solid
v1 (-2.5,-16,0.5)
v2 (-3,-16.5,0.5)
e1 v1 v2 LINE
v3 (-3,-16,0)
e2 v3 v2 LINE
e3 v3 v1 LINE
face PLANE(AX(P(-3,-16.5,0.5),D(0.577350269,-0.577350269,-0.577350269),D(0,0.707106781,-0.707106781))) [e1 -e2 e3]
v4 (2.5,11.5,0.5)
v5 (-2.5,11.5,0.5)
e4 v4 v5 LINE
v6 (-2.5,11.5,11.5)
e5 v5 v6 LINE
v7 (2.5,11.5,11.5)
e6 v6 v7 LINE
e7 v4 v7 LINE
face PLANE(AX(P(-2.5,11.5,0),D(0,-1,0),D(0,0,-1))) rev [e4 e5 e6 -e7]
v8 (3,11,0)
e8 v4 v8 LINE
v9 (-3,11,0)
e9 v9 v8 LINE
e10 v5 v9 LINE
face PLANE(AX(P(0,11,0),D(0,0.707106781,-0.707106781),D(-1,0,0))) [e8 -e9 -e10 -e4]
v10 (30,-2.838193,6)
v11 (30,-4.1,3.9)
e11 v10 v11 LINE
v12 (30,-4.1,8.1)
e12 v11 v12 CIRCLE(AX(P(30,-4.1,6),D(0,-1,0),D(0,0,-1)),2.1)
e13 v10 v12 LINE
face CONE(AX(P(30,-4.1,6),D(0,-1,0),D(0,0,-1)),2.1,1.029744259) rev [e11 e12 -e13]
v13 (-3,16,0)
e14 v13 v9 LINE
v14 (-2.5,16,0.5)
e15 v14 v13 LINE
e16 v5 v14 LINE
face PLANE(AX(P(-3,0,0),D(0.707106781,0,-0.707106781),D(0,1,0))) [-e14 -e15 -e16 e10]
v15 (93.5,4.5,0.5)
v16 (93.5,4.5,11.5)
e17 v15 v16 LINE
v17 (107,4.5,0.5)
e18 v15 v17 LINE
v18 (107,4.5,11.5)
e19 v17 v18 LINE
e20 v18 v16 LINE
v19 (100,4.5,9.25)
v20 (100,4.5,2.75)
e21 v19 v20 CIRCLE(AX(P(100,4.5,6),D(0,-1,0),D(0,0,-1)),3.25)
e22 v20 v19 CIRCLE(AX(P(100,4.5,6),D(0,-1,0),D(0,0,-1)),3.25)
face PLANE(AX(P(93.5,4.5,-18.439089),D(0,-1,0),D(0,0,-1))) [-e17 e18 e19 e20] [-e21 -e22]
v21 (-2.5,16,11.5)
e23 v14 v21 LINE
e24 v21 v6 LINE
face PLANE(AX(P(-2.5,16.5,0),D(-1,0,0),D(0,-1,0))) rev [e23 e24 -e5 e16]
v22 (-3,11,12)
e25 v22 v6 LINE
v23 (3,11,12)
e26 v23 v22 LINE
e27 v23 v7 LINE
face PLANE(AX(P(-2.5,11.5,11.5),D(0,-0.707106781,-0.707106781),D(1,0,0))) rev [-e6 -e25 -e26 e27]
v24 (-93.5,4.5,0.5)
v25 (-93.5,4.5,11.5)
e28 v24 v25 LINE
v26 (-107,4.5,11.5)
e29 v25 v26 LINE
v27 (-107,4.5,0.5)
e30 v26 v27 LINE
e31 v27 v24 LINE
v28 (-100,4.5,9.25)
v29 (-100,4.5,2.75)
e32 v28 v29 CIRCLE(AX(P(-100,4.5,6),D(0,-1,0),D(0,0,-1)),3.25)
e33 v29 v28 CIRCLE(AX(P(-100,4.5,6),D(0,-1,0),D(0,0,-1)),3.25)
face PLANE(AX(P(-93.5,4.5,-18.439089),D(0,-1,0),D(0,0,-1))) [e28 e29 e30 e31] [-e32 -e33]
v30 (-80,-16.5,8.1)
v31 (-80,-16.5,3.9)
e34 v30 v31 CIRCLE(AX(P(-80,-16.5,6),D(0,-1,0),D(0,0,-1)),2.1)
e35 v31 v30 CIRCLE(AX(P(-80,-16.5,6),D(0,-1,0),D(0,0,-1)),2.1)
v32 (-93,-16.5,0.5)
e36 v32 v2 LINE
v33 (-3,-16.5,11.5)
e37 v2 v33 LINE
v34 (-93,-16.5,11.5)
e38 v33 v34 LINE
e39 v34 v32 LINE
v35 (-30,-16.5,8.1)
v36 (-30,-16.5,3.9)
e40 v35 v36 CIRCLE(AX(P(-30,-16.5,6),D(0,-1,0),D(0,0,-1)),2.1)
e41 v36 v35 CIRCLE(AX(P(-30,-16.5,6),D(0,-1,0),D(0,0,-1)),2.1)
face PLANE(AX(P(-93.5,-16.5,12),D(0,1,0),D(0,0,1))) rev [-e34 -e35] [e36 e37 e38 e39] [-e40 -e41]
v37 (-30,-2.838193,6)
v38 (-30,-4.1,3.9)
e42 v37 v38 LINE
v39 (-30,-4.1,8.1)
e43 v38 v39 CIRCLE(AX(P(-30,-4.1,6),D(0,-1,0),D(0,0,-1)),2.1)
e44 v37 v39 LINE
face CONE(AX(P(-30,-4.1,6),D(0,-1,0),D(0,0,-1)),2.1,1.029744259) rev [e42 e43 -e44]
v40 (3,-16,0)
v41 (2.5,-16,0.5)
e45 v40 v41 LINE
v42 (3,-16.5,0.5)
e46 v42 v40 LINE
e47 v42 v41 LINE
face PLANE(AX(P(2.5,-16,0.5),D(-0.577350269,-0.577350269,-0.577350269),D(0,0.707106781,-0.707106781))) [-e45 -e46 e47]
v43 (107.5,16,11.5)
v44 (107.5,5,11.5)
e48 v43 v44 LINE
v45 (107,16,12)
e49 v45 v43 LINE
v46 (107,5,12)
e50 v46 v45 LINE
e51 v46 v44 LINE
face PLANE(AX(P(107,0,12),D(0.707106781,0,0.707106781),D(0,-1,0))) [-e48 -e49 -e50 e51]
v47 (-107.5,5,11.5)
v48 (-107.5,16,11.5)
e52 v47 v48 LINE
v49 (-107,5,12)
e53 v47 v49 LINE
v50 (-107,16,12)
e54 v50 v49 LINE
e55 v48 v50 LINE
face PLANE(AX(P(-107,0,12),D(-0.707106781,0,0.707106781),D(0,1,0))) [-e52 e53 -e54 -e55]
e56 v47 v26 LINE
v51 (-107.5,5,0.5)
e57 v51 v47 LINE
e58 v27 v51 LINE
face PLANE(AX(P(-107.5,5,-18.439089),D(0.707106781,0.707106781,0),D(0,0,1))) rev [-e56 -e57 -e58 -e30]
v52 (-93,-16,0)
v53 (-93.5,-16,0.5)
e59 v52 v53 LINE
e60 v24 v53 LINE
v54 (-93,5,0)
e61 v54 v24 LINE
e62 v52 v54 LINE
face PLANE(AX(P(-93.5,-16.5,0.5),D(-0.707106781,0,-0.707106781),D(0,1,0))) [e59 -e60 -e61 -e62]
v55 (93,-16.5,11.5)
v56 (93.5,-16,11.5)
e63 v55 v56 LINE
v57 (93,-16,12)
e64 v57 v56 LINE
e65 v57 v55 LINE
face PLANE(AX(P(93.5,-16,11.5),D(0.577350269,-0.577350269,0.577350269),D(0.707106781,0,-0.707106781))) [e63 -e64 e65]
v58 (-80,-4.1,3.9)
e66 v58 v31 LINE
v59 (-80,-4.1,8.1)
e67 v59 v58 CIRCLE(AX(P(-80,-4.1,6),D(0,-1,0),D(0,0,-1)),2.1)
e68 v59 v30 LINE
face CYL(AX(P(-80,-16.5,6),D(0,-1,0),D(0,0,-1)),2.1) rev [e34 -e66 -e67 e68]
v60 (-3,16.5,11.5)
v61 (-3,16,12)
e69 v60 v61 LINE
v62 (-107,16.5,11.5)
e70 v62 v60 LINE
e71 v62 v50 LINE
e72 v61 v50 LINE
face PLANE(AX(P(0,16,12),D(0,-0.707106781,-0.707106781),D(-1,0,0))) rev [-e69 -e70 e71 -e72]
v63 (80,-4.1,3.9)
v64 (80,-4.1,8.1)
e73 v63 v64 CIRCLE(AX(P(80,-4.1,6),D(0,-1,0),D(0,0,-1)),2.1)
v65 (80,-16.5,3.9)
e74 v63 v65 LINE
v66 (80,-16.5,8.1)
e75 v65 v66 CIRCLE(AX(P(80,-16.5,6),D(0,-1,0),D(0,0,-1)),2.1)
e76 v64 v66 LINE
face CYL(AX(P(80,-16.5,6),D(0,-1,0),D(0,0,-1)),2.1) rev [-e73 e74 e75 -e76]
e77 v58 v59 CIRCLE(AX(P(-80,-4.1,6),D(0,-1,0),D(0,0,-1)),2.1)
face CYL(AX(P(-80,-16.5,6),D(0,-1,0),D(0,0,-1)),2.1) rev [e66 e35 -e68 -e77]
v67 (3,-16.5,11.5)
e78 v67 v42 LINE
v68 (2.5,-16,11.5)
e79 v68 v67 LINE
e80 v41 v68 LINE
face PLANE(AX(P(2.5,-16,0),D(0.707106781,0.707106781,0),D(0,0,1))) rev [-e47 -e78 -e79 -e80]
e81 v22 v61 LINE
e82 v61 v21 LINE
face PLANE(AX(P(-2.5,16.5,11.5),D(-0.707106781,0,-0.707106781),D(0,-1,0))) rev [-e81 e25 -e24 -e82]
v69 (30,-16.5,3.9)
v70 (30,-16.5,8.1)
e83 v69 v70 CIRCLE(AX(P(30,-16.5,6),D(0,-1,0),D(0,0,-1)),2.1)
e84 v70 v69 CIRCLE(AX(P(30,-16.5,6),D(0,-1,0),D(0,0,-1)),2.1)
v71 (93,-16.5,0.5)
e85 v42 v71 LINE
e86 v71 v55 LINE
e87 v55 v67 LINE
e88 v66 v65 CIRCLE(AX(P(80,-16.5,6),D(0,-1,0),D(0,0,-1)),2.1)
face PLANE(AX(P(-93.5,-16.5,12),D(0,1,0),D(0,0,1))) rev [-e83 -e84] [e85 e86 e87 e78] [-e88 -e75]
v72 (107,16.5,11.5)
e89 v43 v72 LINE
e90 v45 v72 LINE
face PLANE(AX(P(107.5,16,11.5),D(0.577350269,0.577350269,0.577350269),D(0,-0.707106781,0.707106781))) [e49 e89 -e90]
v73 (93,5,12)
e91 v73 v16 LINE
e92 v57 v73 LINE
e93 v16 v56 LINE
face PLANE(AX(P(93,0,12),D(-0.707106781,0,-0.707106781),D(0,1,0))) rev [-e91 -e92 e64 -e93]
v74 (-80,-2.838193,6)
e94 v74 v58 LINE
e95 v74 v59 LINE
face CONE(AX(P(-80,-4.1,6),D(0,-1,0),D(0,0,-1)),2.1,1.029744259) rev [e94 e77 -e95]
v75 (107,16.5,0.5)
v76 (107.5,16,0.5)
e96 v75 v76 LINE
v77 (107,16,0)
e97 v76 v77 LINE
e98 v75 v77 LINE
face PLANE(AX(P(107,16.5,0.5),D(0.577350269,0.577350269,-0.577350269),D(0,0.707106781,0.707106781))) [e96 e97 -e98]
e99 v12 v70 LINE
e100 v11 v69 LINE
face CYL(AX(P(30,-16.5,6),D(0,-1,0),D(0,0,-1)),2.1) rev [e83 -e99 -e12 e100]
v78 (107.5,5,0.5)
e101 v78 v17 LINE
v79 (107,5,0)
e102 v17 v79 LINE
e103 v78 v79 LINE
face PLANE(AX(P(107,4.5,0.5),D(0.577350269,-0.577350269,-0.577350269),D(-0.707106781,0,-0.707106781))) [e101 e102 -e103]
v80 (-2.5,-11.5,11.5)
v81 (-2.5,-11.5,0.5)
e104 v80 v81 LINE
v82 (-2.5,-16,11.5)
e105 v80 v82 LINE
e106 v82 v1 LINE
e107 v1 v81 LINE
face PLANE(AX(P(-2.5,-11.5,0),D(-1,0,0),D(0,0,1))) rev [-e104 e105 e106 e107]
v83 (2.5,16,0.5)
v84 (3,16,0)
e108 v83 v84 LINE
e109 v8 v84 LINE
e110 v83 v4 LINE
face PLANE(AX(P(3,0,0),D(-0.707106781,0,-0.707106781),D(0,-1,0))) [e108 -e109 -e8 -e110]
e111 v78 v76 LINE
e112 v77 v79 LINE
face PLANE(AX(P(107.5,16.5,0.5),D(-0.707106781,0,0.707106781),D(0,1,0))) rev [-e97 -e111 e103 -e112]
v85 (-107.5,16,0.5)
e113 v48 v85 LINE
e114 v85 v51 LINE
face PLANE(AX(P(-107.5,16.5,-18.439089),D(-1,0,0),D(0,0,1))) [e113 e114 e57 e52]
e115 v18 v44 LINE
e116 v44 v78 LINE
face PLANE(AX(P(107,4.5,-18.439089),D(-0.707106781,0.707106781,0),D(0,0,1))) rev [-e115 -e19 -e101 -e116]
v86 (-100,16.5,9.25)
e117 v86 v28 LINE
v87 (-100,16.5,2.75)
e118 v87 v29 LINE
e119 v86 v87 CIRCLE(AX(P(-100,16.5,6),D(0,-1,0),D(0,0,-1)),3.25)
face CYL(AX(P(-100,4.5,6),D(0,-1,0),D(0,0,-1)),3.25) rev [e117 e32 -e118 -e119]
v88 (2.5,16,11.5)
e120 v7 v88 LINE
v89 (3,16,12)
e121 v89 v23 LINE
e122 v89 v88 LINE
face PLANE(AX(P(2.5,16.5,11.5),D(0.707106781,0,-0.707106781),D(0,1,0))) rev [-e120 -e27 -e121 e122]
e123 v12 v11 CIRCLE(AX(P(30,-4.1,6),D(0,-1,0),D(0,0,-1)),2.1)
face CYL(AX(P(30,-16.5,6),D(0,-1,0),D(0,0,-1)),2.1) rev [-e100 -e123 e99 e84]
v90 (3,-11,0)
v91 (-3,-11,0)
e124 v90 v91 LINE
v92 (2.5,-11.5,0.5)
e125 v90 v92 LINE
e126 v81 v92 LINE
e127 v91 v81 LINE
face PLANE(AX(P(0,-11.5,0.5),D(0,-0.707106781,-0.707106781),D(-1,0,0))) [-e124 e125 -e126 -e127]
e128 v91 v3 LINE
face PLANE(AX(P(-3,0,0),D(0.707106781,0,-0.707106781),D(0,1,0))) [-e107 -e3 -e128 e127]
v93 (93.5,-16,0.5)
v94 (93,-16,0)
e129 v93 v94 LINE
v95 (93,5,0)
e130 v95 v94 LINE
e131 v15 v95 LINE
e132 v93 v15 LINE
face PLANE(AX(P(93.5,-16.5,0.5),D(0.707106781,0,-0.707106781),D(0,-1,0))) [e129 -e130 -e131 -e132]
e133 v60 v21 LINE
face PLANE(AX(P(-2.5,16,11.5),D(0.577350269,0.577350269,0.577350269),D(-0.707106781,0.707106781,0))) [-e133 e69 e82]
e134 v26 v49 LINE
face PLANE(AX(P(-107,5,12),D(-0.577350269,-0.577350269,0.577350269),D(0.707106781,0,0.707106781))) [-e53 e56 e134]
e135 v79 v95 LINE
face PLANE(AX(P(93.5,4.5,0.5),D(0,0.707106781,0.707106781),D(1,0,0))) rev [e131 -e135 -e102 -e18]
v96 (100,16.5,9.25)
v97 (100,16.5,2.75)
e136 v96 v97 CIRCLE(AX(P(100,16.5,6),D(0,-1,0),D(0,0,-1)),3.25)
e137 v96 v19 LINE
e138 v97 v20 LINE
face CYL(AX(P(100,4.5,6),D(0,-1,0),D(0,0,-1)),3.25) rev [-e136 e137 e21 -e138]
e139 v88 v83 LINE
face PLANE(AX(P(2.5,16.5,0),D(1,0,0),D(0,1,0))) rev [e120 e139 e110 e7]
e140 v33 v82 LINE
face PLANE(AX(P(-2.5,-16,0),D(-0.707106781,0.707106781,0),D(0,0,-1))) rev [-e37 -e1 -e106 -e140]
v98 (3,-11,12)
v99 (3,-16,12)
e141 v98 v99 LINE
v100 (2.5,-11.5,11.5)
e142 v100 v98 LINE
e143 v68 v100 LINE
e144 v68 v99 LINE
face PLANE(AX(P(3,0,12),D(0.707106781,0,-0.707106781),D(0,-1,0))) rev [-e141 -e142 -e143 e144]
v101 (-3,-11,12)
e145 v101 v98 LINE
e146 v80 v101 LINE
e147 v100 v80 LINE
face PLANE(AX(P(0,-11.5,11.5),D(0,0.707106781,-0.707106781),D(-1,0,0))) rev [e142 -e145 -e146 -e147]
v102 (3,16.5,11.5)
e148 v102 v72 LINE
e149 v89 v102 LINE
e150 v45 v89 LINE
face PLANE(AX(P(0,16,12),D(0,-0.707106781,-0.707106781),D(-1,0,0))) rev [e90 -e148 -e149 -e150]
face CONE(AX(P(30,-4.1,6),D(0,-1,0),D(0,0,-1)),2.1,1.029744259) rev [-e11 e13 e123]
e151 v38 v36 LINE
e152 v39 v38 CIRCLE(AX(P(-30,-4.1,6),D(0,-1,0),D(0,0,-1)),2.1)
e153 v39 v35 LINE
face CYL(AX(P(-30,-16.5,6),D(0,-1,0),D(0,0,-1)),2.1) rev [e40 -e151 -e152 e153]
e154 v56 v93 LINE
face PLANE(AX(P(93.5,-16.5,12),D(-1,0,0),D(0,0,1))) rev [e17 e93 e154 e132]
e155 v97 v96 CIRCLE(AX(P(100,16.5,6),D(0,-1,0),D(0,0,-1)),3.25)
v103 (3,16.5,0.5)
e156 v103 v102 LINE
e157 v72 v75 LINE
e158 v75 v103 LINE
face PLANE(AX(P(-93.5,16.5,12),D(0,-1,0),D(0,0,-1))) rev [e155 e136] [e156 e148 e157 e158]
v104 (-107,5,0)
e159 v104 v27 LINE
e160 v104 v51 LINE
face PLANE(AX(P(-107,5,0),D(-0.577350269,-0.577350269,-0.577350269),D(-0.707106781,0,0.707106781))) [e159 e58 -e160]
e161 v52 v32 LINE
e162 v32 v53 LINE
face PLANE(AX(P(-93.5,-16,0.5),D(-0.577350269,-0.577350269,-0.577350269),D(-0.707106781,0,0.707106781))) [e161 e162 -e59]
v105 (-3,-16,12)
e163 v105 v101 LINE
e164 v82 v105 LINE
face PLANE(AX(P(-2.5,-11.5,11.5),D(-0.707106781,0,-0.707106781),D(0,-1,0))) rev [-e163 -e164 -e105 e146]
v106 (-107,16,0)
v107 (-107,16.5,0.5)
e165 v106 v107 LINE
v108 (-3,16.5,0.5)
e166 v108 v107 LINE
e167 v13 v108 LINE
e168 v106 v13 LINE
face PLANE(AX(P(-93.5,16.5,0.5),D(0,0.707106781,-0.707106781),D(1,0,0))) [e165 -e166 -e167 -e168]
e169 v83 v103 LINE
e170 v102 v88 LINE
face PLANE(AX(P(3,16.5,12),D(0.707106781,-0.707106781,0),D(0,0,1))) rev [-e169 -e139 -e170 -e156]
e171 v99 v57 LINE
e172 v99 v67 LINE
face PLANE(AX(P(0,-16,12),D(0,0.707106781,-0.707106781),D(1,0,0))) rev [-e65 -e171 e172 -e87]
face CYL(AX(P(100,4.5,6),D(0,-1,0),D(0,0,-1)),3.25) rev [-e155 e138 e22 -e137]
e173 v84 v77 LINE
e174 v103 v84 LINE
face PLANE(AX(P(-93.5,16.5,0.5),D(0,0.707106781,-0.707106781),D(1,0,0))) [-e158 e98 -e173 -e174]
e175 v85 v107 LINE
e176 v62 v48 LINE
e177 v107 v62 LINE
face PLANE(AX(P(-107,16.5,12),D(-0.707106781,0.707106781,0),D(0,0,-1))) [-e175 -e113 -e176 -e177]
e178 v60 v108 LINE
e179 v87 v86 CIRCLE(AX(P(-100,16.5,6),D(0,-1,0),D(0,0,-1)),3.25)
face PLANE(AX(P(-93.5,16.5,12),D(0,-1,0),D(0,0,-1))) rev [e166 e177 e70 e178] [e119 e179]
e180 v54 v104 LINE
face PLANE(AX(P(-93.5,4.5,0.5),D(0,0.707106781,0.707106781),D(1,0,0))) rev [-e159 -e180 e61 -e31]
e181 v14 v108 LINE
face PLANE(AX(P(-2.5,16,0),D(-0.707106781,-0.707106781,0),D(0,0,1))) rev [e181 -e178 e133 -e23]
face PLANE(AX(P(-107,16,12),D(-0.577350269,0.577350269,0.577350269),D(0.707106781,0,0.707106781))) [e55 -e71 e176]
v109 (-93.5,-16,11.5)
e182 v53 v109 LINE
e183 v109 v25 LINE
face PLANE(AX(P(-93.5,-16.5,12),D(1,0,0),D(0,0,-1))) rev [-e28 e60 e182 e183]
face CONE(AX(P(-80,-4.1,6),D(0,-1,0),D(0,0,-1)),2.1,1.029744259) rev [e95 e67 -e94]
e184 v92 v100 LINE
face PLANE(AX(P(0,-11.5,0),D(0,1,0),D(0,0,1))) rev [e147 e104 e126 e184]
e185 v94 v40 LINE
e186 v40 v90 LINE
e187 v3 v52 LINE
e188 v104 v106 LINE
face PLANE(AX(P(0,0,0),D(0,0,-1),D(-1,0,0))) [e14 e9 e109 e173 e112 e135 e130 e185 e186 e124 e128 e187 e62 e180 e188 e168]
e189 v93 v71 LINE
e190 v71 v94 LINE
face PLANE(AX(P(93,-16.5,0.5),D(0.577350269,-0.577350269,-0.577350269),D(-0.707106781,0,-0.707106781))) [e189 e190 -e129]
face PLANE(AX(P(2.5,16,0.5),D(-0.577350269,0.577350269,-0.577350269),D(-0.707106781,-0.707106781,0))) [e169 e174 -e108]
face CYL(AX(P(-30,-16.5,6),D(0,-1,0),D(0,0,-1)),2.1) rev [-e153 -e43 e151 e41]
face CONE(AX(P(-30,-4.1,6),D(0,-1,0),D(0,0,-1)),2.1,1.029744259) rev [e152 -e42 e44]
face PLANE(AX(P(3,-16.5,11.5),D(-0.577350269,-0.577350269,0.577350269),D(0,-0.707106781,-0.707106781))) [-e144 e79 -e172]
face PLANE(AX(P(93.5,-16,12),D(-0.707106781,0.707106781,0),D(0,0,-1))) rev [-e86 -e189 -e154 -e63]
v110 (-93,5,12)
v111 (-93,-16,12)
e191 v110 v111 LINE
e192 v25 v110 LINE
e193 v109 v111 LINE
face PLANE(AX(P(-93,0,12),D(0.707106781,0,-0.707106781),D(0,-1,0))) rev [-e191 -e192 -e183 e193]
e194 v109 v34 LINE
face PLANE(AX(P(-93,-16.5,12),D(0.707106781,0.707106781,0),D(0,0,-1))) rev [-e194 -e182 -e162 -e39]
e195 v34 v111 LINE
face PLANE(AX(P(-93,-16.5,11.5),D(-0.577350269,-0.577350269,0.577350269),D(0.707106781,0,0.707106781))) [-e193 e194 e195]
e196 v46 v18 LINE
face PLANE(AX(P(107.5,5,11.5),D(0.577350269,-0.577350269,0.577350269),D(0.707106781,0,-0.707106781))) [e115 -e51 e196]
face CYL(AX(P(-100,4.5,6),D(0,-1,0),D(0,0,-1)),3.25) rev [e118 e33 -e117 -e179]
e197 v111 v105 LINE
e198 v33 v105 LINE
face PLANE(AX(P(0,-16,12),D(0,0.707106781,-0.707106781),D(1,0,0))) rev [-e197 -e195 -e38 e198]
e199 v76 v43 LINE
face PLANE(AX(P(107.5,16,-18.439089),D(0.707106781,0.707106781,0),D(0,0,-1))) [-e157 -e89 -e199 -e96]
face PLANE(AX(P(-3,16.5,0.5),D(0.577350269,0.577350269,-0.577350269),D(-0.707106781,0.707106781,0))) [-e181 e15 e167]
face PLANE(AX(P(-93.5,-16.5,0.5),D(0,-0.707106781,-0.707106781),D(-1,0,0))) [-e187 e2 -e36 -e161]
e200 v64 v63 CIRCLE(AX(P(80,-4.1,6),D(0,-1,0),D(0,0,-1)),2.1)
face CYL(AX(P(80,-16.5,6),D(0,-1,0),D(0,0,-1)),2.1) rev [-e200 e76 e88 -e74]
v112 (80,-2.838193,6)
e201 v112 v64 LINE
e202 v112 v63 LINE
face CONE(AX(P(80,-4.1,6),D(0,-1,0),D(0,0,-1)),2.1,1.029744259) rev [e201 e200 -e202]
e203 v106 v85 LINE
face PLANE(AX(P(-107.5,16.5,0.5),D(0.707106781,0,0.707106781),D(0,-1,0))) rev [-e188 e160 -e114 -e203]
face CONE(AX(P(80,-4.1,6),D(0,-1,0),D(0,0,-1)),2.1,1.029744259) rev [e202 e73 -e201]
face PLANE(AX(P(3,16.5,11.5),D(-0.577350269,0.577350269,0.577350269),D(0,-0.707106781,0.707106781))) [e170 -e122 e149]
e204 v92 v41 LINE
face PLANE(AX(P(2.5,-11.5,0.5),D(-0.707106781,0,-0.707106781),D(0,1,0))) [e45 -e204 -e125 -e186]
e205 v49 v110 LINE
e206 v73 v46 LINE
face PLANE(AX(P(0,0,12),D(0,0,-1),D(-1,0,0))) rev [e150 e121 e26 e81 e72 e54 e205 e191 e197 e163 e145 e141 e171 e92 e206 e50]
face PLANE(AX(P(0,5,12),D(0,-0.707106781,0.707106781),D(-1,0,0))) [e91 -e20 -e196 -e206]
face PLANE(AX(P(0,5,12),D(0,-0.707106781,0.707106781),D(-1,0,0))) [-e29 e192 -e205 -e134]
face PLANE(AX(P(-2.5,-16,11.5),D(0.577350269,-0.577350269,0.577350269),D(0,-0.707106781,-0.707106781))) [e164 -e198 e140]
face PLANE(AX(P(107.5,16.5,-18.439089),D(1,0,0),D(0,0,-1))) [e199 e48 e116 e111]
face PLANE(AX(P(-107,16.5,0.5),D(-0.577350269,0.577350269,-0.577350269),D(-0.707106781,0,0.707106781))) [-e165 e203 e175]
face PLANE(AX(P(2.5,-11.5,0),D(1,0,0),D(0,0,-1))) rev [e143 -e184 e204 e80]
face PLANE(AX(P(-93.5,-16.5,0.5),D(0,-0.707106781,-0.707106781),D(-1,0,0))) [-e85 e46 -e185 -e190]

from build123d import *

# Parameters (mm, degrees)
SKETCH_1_W              = 187
SKETCH_1_H              = 33
EXTRUDE_1_DEPTH         = 12
HOLE_WIZARD_M5_1_D      = 4.2
HOLE_WIZARD_M5_1_DEPTH  = 12.4
HOLE_WIZARD_M5_1_TIP    = 1.2618073
SKETCH_8_W              = 5
SKETCH_8_H              = 12
CUT_EXTRUDE_2_DEPTH     = 5
SKETCH_11_W             = 5
SKETCH_11_H             = 5
CUT_EXTRUDE_3_DEPTH     = 96.700052247
SKETCH_12_W             = 14
SKETCH_12_H             = 12
EXTRUDE_2_DEPTH         = 12
HOLE_WIZARD_6_5_6_5_1_D = 6.5
CHAMFER_1_SIZE          = 0.5


with BuildPart() as part:
    # 草图1 → 凸台-拉伸1 (new body)
    with BuildSketch(Plane.XY):
        Rectangle(SKETCH_1_W, SKETCH_1_H)
    extrude(amount=EXTRUDE_1_DEPTH)

    # M5 螺纹孔1
    with Locations(Plane(origin=(0, -16.5, 0), x_dir=(-1, 0, 0), z_dir=(0, -1, 0))):
        with Locations((-80, -6), (-30, -6), (30, -6), (80, -6)):
            Hole(HOLE_WIZARD_M5_1_D / 2, depth=HOLE_WIZARD_M5_1_DEPTH)
            with Locations((0, 0, -(HOLE_WIZARD_M5_1_DEPTH + HOLE_WIZARD_M5_1_TIP / 2))):  # 118° drill point
                Cone(0, HOLE_WIZARD_M5_1_D / 2, HOLE_WIZARD_M5_1_TIP, mode=Mode.SUBTRACT)

    # 草图8 → 切除-拉伸2 (cut)
    with BuildSketch(Plane.XZ.offset(16.5)):
        with Locations((0, 6)):
            Rectangle(SKETCH_8_W, SKETCH_8_H)
    extrude(amount=-CUT_EXTRUDE_2_DEPTH, mode=Mode.SUBTRACT)

    # 草图11 → 切除-拉伸3 (cut, through all)
    with BuildSketch(Plane.XY.offset(12)):
        with Locations((0, 14)):
            Rectangle(SKETCH_11_W, SKETCH_11_H)
    extrude(amount=-CUT_EXTRUDE_3_DEPTH, mode=Mode.SUBTRACT)

    # 草图12 → 凸台-拉伸2 (add)
    with BuildSketch(Plane.XY.offset(12)):
        with Locations((100.5, 10.5)):
            Rectangle(SKETCH_12_W, SKETCH_12_H)
        with Locations((-100.5, 10.5)):
            Rectangle(SKETCH_12_W, SKETCH_12_H)
    extrude(amount=-EXTRUDE_2_DEPTH)

    # Ø6.5 (6.5) 直径孔1 (through all)
    with Locations(Plane(origin=(0, 4.5, 0), x_dir=(-1, 0, 0), z_dir=(0, -1, 0))):
        with Locations((-100, -6), (100, -6)):
            Hole(HOLE_WIZARD_6_5_6_5_1_D / 2)

    # 倒角1
    chamfer_1_edges = [part.edges().sort_by_distance(p)[0] for p in [
        (-48, -16.5, 12),
        (48, -16.5, 0),
        (48, -16.5, 12),
        (-2.5, -14, 0),
        (0, -11.5, 12),
        (-2.5, -14, 12),
        (2.5, -14, 12),
        (0, -11.5, 0),
        (2.5, -14, 0),
        (-2.5, -16.5, 6),
        (2.5, -16.5, 6),
        (93.5, -6, 12),
        (-48, -16.5, 0),
        (-55, 16.5, 0),
        (-55, 16.5, 12),
        (-2.5, 14, 0),
        (55, 16.5, 0),
        (-2.5, 16.5, 6),
        (2.5, 14, 0),
        (2.5, 16.5, 6),
        (0, 11.5, 0),
        (-2.5, 14, 12),
        (0, 11.5, 12),
        (2.5, 14, 12),
        (93.5, -6, 0),
        (100.5, 4.5, 12),
        (107.5, 10.5, 12),
        (100.5, 4.5, 0),
        (107.5, 4.5, 6),
        (107.5, 10.5, 0),
        (107.5, 16.5, 6),
        (93.5, -16.5, 6),
        (-93.5, -16.5, 6),
        (-93.5, -6, 0),
        (-93.5, -6, 12),
        (-107.5, 10.5, 12),
        (-100.5, 4.5, 12),
        (-107.5, 10.5, 0),
        (-107.5, 4.5, 6),
        (-100.5, 4.5, 0),
        (-107.5, 16.5, 6),
        (55, 16.5, 12),
    ]]
    chamfer(chamfer_1_edges, length=CHAMFER_1_SIZE)


solid = part.part
